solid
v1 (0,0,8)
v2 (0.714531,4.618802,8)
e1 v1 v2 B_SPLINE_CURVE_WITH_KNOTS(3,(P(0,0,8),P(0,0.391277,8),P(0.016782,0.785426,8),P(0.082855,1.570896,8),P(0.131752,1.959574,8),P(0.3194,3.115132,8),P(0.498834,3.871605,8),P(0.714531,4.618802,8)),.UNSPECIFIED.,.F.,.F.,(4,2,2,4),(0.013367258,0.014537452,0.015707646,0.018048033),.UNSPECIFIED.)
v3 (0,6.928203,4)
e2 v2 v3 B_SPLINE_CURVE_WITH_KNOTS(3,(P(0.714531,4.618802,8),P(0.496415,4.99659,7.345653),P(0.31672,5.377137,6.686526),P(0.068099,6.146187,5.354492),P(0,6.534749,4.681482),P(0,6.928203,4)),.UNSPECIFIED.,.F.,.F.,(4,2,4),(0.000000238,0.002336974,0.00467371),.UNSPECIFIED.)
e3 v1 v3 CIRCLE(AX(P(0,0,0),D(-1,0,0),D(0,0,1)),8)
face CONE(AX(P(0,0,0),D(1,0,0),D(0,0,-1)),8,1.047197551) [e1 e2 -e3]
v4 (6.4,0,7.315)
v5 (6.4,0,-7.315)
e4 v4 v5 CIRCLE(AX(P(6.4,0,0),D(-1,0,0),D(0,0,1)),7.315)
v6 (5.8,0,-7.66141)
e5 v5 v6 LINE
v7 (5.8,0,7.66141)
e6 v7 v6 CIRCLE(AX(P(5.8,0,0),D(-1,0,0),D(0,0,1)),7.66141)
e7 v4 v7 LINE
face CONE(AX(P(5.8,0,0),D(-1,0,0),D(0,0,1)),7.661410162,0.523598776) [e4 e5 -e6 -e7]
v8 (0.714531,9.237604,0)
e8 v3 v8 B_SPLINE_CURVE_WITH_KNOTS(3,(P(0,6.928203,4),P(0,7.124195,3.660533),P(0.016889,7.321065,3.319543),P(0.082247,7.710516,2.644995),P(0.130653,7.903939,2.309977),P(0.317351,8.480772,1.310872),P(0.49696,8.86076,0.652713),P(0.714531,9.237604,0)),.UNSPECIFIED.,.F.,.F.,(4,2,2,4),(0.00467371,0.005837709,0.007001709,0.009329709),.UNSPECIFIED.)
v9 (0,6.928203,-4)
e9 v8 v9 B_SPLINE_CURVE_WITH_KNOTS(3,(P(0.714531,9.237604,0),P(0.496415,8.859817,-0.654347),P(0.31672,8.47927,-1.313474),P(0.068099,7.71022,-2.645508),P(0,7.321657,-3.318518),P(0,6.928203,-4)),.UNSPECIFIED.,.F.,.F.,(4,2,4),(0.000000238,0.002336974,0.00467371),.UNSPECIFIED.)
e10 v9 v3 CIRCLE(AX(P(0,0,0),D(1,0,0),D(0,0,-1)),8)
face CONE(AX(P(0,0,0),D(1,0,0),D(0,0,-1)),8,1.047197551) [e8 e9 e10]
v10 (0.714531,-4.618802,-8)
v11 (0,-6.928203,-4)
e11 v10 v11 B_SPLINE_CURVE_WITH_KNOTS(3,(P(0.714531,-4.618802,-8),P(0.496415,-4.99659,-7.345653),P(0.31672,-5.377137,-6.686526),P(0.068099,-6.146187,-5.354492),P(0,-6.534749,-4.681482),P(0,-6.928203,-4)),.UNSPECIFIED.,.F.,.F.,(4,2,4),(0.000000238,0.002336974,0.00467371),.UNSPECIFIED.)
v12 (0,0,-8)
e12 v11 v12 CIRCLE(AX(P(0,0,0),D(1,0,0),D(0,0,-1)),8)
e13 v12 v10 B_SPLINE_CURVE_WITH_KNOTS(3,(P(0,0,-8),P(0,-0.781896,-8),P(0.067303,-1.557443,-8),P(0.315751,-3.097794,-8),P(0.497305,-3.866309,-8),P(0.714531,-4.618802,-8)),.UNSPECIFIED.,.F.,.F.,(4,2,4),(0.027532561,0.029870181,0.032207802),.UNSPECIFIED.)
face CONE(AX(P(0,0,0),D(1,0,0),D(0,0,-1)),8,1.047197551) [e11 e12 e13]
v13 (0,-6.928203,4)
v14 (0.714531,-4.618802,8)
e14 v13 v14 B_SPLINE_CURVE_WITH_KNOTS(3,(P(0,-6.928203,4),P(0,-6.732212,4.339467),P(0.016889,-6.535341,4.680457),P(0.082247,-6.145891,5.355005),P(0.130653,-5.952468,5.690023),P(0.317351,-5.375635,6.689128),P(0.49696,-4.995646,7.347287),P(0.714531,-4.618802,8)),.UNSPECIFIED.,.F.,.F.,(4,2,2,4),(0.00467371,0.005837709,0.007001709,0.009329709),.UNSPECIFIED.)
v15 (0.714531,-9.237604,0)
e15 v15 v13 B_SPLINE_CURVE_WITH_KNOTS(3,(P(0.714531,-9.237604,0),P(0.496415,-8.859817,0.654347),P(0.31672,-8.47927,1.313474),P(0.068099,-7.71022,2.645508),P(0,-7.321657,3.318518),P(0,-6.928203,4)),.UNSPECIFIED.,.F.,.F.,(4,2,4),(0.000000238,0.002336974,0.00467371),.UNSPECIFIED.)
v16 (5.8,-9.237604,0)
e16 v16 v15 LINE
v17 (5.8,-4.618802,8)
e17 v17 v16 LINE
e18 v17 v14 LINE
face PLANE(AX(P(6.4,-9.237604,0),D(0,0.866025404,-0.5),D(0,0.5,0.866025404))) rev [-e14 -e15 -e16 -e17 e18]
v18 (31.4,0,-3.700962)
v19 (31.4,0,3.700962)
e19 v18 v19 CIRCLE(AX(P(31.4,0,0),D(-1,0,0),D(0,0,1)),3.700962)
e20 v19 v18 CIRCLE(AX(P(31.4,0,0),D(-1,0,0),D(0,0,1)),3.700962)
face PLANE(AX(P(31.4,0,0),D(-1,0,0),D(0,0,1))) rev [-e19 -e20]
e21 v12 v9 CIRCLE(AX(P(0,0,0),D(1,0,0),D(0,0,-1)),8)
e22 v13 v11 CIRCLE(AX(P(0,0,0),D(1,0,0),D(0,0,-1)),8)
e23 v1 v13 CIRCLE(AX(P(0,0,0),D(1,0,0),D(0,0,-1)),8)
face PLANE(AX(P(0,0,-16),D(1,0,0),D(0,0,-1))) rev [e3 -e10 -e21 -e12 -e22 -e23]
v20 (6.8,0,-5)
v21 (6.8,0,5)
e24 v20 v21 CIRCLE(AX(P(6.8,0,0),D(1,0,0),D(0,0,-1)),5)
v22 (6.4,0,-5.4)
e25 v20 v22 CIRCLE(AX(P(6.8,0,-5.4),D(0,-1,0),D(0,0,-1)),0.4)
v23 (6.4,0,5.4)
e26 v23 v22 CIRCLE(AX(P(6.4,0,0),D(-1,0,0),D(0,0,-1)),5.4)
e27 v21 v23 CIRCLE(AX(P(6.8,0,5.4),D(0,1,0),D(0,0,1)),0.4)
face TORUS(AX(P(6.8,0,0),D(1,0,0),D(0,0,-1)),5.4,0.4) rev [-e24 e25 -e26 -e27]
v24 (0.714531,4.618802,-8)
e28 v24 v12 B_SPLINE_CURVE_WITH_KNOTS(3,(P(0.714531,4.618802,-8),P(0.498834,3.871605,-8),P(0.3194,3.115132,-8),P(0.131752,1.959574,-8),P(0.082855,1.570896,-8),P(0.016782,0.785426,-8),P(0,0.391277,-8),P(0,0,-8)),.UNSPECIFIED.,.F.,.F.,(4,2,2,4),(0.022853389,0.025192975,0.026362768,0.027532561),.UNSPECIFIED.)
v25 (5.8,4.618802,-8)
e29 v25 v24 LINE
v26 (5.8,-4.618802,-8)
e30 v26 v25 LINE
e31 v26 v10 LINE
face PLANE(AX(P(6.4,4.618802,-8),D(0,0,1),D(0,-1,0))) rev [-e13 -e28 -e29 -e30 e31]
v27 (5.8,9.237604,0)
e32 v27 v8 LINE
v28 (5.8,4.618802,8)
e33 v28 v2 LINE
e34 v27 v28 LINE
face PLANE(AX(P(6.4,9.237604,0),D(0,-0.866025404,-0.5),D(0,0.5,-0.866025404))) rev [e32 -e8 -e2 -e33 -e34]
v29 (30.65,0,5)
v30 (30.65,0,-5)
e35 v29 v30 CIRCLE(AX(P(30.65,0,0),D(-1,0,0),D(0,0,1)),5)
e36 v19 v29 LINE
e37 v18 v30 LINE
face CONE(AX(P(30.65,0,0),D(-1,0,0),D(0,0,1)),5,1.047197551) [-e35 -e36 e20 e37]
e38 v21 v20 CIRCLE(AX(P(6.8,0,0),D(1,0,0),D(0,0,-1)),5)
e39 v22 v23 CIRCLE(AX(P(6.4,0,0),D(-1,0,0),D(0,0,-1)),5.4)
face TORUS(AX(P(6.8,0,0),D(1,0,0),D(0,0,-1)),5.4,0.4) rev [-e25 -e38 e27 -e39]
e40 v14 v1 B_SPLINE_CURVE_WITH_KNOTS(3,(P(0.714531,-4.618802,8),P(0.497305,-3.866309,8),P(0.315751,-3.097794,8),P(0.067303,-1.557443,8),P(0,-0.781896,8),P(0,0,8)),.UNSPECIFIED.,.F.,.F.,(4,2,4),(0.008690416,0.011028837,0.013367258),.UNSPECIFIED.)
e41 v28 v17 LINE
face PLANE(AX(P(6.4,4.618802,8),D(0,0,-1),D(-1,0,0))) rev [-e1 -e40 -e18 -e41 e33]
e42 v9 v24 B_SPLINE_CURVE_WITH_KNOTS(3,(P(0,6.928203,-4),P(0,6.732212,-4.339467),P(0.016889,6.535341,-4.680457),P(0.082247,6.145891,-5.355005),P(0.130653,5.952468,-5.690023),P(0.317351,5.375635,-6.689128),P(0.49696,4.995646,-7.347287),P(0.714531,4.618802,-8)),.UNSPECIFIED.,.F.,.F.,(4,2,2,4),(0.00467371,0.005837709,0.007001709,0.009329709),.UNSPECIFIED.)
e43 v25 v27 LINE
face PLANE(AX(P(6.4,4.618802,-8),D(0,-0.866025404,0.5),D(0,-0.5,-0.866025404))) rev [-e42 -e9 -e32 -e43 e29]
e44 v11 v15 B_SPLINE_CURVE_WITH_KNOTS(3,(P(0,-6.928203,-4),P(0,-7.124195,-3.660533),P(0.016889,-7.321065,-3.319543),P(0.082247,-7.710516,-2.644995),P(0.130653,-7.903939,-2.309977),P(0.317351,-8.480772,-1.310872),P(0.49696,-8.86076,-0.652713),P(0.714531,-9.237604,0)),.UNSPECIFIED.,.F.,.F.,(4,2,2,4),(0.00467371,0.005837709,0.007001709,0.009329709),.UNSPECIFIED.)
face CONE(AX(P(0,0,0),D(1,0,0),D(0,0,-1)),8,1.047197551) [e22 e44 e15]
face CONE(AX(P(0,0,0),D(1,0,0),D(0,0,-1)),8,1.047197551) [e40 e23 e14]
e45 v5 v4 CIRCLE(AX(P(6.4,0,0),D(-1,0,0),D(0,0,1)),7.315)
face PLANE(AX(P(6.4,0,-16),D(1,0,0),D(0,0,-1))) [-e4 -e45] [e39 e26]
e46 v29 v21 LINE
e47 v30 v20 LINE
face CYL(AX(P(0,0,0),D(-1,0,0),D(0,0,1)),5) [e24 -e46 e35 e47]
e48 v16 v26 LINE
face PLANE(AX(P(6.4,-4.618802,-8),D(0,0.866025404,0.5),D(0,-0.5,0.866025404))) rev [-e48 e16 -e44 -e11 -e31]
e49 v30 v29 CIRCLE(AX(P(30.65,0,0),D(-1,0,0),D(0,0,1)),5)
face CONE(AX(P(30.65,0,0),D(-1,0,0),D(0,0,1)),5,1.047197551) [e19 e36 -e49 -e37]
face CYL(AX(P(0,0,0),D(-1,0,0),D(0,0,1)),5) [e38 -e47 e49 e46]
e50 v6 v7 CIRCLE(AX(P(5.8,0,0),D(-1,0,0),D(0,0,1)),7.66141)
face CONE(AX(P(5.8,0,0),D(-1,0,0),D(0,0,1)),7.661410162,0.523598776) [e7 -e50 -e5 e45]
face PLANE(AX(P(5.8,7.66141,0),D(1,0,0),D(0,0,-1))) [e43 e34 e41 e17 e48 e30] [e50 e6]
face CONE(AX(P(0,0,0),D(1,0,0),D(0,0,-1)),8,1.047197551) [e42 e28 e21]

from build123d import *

# Parameters (mm, degrees)
EXTRUDE_390_DEPTH = 6.4
FILLET_1290_R     = 0.4


with BuildPart() as part:
    # 草图1 → Extrude 390 (new body)
    with BuildSketch(Plane(origin=(0, 0, 0), x_dir=(0, 0, -1), z_dir=(1, 0, 0))):
        Polygon((8, 4.618802154), (8, -4.618802154), (0, -9.237604307), (-8, -4.618802154), (-8, 4.618802154), (0, 9.237604307), align=None)
    extrude(amount=EXTRUDE_390_DEPTH)

    # 草图2 → 凸台-旋转1 (revolve)
    with BuildSketch(Plane.XY, mode=Mode.PRIVATE) as revolve_1_sk:
        Polygon((0, 0), (31.4, 0), (31.4, 3.701), (31.4, 5), (0, 5), align=None)
    revolve(revolve_1_sk.sketch.rotate(Axis((0, 0, 0), (1, 0, 0)), 90), axis=Axis((0, 0, 0), (1, 0, 0)))

    # 草图3 → 切除-旋转1 (revolve, cut)
    with BuildSketch(Plane.XY):
        Polygon((0, 8), (3.601282526, 14.237604307), (3.601282526, 19.237604307), (-10, 19.237604307), (-10, 8), align=None)
    revolve(axis=Axis((0, 0, 0), (1, 0, 0)), mode=Mode.SUBTRACT)

    # 草图4 → 切除-旋转3 (revolve, cut)
    with BuildSketch(Plane.XY, mode=Mode.PRIVATE) as cut_revolve_3_sk:
        Polygon((6.4, 7.315), (5.8, 7.661410162), (5.8, 9.237604307), (6.4, 9.237604307), align=None)
    revolve(cut_revolve_3_sk.sketch.rotate(Axis((0, 0, 0), (1, 0, 0)), 90), axis=Axis((0, 0, 0), (1, 0, 0)), mode=Mode.SUBTRACT)

    # Fillet 1290
    fillet_1290_edges = [part.edges().sort_by_distance(p)[0] for p in [
        (6.4, 0, -5),
    ]]
    fillet(fillet_1290_edges, radius=FILLET_1290_R)

    # 草图6 → 切除-旋转4 (revolve, cut)
    with BuildSketch(Plane.XY, mode=Mode.PRIVATE) as cut_revolve_4_sk:
        Polygon((30.65, 5), (32.15, 5), (31.4, 3.700961894), align=None)
    revolve(cut_revolve_4_sk.sketch.rotate(Axis((0, 0, 0), (1, 0, 0)), 90), axis=Axis((0, 0, 0), (1, 0, 0)), mode=Mode.SUBTRACT)


solid = part.part
